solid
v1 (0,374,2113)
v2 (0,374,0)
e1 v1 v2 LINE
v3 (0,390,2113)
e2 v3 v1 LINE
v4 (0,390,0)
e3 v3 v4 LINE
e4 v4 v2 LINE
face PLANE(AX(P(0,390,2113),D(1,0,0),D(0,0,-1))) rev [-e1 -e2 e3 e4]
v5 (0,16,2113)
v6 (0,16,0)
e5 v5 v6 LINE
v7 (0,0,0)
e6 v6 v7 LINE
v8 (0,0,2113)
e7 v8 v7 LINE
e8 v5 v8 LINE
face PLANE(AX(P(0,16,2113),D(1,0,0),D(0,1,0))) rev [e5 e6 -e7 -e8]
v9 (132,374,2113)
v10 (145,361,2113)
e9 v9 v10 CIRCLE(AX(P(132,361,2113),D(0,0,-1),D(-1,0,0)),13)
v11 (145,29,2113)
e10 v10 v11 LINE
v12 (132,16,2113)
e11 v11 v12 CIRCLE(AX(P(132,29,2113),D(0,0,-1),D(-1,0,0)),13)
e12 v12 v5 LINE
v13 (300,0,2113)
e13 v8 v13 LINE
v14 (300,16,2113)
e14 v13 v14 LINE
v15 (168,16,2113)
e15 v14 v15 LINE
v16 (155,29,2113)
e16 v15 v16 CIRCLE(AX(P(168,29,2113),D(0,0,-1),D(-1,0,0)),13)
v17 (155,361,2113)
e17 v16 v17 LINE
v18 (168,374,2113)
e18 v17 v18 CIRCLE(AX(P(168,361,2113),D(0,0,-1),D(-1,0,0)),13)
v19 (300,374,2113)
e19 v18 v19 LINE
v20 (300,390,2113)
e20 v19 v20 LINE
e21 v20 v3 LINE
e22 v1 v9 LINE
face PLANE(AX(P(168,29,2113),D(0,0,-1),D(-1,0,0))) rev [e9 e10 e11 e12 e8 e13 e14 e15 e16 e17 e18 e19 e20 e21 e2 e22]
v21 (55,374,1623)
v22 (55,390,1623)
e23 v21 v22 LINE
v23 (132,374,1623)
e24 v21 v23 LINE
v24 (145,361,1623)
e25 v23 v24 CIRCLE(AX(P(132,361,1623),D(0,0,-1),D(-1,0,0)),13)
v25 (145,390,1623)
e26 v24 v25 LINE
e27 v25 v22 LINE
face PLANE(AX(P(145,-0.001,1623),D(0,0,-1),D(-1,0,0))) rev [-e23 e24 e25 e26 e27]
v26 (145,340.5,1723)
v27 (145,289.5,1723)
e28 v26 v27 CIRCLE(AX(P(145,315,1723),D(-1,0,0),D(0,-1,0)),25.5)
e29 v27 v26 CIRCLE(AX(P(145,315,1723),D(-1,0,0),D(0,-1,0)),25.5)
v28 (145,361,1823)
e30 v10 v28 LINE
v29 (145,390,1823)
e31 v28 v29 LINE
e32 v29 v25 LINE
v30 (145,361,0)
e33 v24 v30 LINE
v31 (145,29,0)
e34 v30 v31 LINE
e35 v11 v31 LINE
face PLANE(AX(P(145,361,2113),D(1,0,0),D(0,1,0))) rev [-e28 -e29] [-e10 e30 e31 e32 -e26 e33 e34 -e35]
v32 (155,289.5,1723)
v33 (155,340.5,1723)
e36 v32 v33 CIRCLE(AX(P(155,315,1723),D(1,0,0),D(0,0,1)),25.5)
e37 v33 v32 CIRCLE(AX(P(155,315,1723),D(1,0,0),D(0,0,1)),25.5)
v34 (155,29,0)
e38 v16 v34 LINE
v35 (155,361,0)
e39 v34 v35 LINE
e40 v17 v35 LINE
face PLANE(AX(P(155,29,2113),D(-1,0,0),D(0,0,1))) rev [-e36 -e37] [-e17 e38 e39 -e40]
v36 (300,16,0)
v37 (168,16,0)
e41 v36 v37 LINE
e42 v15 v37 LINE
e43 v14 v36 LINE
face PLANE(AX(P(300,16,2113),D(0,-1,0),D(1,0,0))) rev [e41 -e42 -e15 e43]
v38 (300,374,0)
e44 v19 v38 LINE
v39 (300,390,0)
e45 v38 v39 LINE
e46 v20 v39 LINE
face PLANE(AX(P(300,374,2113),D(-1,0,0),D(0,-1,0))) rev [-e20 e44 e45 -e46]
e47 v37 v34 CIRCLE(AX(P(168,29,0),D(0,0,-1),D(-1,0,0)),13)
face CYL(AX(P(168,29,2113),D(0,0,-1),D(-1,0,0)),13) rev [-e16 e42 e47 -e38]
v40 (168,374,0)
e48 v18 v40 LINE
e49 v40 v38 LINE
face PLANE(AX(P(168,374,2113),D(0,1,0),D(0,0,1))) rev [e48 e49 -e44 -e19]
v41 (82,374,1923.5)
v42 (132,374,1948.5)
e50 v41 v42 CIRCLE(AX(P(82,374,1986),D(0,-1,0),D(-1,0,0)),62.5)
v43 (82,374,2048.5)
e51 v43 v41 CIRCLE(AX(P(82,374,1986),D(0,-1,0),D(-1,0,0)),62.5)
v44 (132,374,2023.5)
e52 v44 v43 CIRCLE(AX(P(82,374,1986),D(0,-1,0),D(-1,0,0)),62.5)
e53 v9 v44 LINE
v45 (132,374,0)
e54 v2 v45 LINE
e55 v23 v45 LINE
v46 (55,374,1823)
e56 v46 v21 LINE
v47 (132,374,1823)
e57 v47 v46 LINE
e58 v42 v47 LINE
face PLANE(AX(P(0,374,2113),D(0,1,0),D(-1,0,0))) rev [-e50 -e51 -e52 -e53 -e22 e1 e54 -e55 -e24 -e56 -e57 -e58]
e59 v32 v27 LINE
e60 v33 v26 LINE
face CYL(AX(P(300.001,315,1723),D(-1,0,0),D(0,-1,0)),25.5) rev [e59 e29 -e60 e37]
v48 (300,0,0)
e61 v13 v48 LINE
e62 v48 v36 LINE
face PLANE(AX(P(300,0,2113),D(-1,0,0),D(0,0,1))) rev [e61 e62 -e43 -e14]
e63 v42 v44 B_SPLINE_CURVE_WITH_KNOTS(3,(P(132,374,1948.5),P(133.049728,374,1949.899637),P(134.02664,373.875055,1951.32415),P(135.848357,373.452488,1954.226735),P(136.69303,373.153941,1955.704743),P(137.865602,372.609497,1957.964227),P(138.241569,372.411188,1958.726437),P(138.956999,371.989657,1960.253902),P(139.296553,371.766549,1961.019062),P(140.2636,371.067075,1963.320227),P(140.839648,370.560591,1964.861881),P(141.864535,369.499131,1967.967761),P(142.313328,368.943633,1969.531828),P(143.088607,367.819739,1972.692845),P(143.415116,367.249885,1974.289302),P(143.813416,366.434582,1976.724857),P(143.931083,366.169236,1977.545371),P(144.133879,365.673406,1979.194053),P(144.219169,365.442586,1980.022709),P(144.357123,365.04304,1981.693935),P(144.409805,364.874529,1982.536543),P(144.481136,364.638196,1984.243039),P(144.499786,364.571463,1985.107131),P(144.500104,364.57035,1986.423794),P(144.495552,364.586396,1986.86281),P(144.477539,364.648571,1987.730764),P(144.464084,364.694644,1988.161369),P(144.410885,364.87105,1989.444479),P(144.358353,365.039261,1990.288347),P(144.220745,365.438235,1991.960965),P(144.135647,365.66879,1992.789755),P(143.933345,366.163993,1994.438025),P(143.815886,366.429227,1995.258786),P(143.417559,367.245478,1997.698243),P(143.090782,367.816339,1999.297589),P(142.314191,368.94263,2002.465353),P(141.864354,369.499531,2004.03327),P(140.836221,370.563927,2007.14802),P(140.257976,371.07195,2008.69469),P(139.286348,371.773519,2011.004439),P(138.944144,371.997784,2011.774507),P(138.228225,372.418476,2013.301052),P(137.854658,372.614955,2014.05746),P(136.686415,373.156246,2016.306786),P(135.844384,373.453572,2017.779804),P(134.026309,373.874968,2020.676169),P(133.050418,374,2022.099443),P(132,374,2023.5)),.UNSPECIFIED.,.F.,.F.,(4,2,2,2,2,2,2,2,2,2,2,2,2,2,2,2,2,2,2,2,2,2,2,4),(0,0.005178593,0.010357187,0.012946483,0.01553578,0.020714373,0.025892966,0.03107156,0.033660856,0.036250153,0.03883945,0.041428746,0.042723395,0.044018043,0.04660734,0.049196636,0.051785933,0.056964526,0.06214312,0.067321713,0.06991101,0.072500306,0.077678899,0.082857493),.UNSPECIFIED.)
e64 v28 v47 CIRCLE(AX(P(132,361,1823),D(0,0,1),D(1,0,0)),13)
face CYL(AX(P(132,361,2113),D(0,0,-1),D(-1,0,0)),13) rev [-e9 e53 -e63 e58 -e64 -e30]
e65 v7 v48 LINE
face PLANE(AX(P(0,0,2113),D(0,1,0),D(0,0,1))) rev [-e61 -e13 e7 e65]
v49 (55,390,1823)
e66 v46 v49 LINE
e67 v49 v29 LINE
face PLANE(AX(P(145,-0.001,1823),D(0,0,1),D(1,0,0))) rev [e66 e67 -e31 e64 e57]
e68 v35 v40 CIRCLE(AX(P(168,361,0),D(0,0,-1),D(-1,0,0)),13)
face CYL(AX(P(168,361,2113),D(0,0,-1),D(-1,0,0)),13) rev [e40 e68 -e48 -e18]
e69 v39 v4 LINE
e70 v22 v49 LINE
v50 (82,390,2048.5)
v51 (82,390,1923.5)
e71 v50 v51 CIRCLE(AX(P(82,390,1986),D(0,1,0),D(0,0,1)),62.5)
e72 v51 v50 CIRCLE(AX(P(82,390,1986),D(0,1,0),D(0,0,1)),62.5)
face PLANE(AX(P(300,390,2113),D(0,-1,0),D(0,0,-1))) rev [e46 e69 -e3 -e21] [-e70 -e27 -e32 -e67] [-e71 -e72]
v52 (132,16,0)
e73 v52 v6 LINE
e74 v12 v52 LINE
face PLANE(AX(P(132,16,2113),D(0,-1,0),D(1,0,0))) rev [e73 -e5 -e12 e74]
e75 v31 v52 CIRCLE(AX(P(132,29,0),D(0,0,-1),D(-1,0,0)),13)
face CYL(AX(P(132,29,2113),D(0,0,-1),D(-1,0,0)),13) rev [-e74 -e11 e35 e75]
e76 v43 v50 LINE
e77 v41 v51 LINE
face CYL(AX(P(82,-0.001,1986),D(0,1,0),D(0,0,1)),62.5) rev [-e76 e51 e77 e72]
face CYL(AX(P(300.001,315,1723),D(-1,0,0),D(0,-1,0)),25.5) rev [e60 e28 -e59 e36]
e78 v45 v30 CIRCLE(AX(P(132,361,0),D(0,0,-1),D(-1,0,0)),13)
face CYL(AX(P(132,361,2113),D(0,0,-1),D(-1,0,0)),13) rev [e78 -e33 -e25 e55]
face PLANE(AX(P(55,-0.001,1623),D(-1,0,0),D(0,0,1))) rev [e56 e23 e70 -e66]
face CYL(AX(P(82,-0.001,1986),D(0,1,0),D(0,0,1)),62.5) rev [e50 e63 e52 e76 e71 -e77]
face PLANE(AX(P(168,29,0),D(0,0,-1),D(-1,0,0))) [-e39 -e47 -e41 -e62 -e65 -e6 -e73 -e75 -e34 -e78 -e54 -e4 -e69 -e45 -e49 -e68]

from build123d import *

# Parameters (mm, degrees)
BOSS_EXTRUDE1_DEPTH = 2113
CUT_EXTRUDE1_REACH  = 2171.532
SKETCH2_R           = 62.5
SKETCH2_W           = 90
SKETCH2_H           = 200
CUT_EXTRUDE2_REACH  = 2156.273
SKETCH3_R           = 25.5


with BuildPart() as part:
    # Sketch1 → Boss-Extrude1 (new body)
    with BuildSketch(Plane.XY):
        with BuildLine():
            Line((0, 0), (300, 0))
            Line((300, 0), (300, 16))
            Line((300, 16), (168, 16))
            ThreePointArc((168, 16), (158.807611845, 19.807611845), (155, 29))
            Line((155, 29), (155, 361))
            ThreePointArc((155, 361), (158.807611845, 370.192388155), (168, 374))
            Line((168, 374), (300, 374))
            Line((300, 374), (300, 390))
            Line((300, 390), (0, 390))
            Line((0, 390), (0, 374))
            Line((0, 374), (132, 374))
            ThreePointArc((132, 374), (141.192388155, 370.192388155), (145, 361))
            Line((145, 361), (145, 29))
            ThreePointArc((145, 29), (141.192388155, 19.807611845), (132, 16))
            Line((132, 16), (0, 16))
            Line((0, 16), (0, 0))
        make_face()
    extrude(amount=BOSS_EXTRUDE1_DEPTH)

    # Sketch2 → Cut-Extrude1 (cut, up to next)
    with BuildSketch(Plane(origin=(0, 390, 0), x_dir=(1, 0, 0), z_dir=(0, 1, 0)), mode=Mode.PRIVATE) as cut_extrude1_sk1:
        with Locations(Location((82, -1986, 0), (0, 0, 270))):
            Circle(SKETCH2_R)
    cut_extrude1_tool1 = extrude(cut_extrude1_sk1.sketch, amount=-CUT_EXTRUDE1_REACH, mode=Mode.PRIVATE) & part.part
    # Sketch2 → Cut-Extrude1 (cut, up to next)
    with BuildSketch(Plane(origin=(0, 390, 0), x_dir=(1, 0, 0), z_dir=(0, 1, 0)), mode=Mode.PRIVATE) as cut_extrude1_sk2:
        with Locations((100, -1723)):
            Rectangle(SKETCH2_W, SKETCH2_H)
    cut_extrude1_tool2 = extrude(cut_extrude1_sk2.sketch, amount=-CUT_EXTRUDE1_REACH, mode=Mode.PRIVATE) & part.part
    add(cut_extrude1_tool1.solids().sort_by_distance((82, 390, 1986))[0], mode=Mode.SUBTRACT)
    add(cut_extrude1_tool2.solids().sort_by_distance((100, 390, 1723))[0], mode=Mode.SUBTRACT)

    # Sketch3 → Cut-Extrude2 (cut, up to next)
    with BuildSketch(Plane.ZY.offset(-145), mode=Mode.PRIVATE) as cut_extrude2_sk1:
        with Locations(Location((1723, 315, 0), (0, 0, 270))):
            Circle(SKETCH3_R)
    cut_extrude2_tool1 = extrude(cut_extrude2_sk1.sketch, amount=-CUT_EXTRUDE2_REACH, mode=Mode.PRIVATE) & part.part
    add(cut_extrude2_tool1.solids().sort_by_distance((145, 315, 1723))[0], mode=Mode.SUBTRACT)


solid = part.part
